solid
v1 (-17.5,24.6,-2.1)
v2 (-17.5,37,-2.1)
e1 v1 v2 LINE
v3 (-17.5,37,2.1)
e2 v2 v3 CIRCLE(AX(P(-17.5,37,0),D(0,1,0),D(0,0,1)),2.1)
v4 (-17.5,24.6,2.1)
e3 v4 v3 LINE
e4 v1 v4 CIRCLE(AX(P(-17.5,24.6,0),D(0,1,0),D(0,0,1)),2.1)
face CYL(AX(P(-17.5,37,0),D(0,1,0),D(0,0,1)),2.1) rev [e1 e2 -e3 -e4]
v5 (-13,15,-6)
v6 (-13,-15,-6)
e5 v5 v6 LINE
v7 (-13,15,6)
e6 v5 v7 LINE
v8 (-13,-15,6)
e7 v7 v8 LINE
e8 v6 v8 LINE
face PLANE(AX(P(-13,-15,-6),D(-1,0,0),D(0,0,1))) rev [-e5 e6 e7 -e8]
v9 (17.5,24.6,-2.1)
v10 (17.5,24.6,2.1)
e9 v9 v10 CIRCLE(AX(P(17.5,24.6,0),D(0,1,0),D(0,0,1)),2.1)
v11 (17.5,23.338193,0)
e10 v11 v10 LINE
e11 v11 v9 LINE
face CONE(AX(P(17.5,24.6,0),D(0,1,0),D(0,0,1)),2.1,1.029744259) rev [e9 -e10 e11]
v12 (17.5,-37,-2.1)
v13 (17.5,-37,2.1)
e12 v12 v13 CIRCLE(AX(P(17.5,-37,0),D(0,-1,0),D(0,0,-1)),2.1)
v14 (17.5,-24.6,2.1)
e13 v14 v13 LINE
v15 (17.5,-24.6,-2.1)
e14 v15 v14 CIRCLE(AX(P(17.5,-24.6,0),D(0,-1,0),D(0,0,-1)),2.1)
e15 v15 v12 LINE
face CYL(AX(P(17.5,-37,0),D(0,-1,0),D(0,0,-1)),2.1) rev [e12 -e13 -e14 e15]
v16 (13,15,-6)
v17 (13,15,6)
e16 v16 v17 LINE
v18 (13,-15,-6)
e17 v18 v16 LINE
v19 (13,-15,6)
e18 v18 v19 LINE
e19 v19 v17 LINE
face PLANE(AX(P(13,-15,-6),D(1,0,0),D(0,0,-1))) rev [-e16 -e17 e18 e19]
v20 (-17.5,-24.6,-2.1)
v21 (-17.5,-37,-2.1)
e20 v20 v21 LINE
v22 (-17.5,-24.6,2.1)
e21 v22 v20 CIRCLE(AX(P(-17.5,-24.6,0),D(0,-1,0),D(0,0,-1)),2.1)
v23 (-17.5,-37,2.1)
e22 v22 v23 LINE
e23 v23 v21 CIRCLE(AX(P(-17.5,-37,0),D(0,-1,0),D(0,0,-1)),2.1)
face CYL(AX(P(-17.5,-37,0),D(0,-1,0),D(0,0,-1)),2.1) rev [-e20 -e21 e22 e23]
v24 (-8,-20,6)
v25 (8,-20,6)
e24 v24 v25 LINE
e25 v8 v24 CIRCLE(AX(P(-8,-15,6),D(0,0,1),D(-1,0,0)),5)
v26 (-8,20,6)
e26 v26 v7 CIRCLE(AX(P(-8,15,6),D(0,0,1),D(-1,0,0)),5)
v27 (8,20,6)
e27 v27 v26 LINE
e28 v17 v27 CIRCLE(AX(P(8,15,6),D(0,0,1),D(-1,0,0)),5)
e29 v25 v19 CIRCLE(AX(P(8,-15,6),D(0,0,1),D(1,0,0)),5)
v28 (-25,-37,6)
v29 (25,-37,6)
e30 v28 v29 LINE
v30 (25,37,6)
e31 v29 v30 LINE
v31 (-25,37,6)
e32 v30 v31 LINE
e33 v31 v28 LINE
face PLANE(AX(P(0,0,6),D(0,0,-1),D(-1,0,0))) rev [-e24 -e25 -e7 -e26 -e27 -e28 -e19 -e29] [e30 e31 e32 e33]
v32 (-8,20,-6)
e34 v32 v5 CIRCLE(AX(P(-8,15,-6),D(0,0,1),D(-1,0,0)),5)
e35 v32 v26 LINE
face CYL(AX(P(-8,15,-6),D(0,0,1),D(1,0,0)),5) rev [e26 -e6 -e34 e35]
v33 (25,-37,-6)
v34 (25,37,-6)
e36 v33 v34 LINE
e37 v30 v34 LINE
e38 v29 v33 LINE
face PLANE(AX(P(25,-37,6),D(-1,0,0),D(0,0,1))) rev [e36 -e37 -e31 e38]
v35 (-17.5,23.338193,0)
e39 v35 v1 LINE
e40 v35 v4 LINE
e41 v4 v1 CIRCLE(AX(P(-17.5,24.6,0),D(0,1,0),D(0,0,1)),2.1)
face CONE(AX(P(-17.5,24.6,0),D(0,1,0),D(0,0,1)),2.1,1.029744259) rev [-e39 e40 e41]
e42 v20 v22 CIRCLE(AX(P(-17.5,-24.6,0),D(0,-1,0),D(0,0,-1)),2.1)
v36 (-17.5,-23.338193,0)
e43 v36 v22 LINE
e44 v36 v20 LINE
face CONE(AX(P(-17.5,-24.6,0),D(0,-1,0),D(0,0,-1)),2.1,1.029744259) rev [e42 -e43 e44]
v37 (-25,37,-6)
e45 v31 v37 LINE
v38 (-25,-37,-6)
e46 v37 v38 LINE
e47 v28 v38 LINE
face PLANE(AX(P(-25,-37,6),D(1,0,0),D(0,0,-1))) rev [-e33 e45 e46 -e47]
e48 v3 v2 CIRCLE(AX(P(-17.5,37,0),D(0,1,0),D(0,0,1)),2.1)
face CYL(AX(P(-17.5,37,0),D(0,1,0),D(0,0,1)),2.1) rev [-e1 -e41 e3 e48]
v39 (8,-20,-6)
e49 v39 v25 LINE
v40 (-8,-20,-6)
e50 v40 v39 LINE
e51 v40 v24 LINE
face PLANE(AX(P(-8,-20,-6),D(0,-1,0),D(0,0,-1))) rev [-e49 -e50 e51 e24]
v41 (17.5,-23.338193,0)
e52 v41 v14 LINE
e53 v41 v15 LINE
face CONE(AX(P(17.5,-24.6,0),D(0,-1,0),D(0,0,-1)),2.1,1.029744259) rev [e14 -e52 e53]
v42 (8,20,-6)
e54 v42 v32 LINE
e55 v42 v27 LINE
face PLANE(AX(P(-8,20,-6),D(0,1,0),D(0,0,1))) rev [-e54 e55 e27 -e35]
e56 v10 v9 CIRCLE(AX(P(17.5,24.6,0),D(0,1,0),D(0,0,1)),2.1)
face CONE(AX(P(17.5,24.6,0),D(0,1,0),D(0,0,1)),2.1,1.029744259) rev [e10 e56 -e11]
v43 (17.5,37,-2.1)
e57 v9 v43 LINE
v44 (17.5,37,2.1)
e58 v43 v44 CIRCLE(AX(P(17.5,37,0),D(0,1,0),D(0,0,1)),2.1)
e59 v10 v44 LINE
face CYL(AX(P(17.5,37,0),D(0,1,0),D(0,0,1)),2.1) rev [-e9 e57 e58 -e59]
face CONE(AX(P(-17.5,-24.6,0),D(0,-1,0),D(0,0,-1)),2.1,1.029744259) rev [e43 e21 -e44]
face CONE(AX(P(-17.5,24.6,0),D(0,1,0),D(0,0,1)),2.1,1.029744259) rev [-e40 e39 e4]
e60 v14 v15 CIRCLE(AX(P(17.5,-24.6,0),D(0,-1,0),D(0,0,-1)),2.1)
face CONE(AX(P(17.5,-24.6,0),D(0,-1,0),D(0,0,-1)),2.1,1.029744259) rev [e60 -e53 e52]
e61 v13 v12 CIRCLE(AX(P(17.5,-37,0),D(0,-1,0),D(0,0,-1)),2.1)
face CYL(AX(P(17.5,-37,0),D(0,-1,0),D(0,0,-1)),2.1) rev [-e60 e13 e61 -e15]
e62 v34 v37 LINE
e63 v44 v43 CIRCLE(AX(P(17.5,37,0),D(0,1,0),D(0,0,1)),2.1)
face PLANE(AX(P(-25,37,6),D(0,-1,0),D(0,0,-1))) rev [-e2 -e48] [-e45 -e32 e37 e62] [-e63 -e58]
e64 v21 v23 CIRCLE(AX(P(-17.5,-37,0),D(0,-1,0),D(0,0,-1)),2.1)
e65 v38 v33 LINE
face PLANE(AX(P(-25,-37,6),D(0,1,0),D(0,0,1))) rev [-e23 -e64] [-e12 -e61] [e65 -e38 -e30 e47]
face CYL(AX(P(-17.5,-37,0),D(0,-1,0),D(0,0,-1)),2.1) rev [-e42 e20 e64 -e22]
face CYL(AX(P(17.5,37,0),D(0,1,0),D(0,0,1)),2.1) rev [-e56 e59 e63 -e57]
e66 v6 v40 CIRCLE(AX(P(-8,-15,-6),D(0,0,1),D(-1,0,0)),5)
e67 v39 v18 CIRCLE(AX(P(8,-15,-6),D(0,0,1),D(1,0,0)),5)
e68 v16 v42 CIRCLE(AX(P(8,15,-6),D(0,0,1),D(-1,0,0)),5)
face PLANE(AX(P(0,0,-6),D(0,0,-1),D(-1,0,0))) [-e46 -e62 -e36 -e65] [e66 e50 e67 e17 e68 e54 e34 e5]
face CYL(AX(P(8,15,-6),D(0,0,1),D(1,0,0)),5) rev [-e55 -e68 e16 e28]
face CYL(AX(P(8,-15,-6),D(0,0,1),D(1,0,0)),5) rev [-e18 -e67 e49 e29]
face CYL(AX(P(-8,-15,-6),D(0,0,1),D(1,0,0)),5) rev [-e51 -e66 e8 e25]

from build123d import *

# Parameters (mm, degrees)
SKETCH_1_W                  = 50
SKETCH_1_H                  = 74
EXTRUDE_1_DEPTH             = 6
HOLE_WIZARD_M5_1_AT_2_COUNT = 2
HOLE_WIZARD_M5_1_AT_2_PITCH = 35
CUT_EXTRUDE_1_DEPTH         = 47.238512087


with BuildPart() as part:
    # 草图1 → 凸台-拉伸1 (new, symmetric)
    with BuildSketch(Plane.XY):
        Rectangle(SKETCH_1_W, SKETCH_1_H)
    extrude(amount=EXTRUDE_1_DEPTH, both=True)

    # 草图3 → M5 螺纹孔1 (revolve, cut)
    with BuildSketch(Plane(origin=(-17.5, -37, 0), x_dir=(0, 0, -1), z_dir=(1, 0, 0))):
        Polygon((0, 0), (0, 13.6618073), (2.1, 12.4), (2.1, 0), align=None)
    hole_wizard_m5_1 = revolve(axis=Axis((-17.5, -43.35, 0), (0, 1, 0)), mode=Mode.SUBTRACT)

    # M5 螺纹孔1 at 2: M5 螺纹孔1 ×2
    with Locations(*[(i * HOLE_WIZARD_M5_1_AT_2_PITCH, 0, 0) for i in range(1, HOLE_WIZARD_M5_1_AT_2_COUNT)]):
        add(hole_wizard_m5_1, mode=Mode.SUBTRACT)

    # 镜向1: M5 螺纹孔1 across plane
    add(hole_wizard_m5_1.mirror(Plane.ZX), mode=Mode.SUBTRACT)

    # 镜向1 copy 1 sketch → 镜向1 copy 1 (revolve, cut)
    with BuildSketch(Plane(origin=(17.5, 37, 0), x_dir=(0, 0, -1), z_dir=(1, 0, 0))):
        Polygon((0, 0), (0, -13.6618073), (2.1, -12.4), (2.1, 0), align=None)
    revolve(axis=Axis((17.5, 43.35, 0), (0, 1, 0)), mode=Mode.SUBTRACT)

    # 草图5 → 切除-拉伸1 (cut, through all)
    with BuildSketch(Plane.XY.offset(6)):
        with BuildLine():
            Line((-8, -20), (8, -20))
            ThreePointArc((8, -20), (11.535533906, -18.535533906), (13, -15))
            Line((13, -15), (13, 15))
            ThreePointArc((13, 15), (11.535533906, 18.535533906), (8, 20))
            Line((8, 20), (-8, 20))
            ThreePointArc((-8, 20), (-11.535533906, 18.535533906), (-13, 15))
            Line((-13, 15), (-13, -15))
            ThreePointArc((-13, -15), (-11.535533906, -18.535533906), (-8, -20))
        make_face()
    extrude(amount=-CUT_EXTRUDE_1_DEPTH, mode=Mode.SUBTRACT)


solid = part.part
